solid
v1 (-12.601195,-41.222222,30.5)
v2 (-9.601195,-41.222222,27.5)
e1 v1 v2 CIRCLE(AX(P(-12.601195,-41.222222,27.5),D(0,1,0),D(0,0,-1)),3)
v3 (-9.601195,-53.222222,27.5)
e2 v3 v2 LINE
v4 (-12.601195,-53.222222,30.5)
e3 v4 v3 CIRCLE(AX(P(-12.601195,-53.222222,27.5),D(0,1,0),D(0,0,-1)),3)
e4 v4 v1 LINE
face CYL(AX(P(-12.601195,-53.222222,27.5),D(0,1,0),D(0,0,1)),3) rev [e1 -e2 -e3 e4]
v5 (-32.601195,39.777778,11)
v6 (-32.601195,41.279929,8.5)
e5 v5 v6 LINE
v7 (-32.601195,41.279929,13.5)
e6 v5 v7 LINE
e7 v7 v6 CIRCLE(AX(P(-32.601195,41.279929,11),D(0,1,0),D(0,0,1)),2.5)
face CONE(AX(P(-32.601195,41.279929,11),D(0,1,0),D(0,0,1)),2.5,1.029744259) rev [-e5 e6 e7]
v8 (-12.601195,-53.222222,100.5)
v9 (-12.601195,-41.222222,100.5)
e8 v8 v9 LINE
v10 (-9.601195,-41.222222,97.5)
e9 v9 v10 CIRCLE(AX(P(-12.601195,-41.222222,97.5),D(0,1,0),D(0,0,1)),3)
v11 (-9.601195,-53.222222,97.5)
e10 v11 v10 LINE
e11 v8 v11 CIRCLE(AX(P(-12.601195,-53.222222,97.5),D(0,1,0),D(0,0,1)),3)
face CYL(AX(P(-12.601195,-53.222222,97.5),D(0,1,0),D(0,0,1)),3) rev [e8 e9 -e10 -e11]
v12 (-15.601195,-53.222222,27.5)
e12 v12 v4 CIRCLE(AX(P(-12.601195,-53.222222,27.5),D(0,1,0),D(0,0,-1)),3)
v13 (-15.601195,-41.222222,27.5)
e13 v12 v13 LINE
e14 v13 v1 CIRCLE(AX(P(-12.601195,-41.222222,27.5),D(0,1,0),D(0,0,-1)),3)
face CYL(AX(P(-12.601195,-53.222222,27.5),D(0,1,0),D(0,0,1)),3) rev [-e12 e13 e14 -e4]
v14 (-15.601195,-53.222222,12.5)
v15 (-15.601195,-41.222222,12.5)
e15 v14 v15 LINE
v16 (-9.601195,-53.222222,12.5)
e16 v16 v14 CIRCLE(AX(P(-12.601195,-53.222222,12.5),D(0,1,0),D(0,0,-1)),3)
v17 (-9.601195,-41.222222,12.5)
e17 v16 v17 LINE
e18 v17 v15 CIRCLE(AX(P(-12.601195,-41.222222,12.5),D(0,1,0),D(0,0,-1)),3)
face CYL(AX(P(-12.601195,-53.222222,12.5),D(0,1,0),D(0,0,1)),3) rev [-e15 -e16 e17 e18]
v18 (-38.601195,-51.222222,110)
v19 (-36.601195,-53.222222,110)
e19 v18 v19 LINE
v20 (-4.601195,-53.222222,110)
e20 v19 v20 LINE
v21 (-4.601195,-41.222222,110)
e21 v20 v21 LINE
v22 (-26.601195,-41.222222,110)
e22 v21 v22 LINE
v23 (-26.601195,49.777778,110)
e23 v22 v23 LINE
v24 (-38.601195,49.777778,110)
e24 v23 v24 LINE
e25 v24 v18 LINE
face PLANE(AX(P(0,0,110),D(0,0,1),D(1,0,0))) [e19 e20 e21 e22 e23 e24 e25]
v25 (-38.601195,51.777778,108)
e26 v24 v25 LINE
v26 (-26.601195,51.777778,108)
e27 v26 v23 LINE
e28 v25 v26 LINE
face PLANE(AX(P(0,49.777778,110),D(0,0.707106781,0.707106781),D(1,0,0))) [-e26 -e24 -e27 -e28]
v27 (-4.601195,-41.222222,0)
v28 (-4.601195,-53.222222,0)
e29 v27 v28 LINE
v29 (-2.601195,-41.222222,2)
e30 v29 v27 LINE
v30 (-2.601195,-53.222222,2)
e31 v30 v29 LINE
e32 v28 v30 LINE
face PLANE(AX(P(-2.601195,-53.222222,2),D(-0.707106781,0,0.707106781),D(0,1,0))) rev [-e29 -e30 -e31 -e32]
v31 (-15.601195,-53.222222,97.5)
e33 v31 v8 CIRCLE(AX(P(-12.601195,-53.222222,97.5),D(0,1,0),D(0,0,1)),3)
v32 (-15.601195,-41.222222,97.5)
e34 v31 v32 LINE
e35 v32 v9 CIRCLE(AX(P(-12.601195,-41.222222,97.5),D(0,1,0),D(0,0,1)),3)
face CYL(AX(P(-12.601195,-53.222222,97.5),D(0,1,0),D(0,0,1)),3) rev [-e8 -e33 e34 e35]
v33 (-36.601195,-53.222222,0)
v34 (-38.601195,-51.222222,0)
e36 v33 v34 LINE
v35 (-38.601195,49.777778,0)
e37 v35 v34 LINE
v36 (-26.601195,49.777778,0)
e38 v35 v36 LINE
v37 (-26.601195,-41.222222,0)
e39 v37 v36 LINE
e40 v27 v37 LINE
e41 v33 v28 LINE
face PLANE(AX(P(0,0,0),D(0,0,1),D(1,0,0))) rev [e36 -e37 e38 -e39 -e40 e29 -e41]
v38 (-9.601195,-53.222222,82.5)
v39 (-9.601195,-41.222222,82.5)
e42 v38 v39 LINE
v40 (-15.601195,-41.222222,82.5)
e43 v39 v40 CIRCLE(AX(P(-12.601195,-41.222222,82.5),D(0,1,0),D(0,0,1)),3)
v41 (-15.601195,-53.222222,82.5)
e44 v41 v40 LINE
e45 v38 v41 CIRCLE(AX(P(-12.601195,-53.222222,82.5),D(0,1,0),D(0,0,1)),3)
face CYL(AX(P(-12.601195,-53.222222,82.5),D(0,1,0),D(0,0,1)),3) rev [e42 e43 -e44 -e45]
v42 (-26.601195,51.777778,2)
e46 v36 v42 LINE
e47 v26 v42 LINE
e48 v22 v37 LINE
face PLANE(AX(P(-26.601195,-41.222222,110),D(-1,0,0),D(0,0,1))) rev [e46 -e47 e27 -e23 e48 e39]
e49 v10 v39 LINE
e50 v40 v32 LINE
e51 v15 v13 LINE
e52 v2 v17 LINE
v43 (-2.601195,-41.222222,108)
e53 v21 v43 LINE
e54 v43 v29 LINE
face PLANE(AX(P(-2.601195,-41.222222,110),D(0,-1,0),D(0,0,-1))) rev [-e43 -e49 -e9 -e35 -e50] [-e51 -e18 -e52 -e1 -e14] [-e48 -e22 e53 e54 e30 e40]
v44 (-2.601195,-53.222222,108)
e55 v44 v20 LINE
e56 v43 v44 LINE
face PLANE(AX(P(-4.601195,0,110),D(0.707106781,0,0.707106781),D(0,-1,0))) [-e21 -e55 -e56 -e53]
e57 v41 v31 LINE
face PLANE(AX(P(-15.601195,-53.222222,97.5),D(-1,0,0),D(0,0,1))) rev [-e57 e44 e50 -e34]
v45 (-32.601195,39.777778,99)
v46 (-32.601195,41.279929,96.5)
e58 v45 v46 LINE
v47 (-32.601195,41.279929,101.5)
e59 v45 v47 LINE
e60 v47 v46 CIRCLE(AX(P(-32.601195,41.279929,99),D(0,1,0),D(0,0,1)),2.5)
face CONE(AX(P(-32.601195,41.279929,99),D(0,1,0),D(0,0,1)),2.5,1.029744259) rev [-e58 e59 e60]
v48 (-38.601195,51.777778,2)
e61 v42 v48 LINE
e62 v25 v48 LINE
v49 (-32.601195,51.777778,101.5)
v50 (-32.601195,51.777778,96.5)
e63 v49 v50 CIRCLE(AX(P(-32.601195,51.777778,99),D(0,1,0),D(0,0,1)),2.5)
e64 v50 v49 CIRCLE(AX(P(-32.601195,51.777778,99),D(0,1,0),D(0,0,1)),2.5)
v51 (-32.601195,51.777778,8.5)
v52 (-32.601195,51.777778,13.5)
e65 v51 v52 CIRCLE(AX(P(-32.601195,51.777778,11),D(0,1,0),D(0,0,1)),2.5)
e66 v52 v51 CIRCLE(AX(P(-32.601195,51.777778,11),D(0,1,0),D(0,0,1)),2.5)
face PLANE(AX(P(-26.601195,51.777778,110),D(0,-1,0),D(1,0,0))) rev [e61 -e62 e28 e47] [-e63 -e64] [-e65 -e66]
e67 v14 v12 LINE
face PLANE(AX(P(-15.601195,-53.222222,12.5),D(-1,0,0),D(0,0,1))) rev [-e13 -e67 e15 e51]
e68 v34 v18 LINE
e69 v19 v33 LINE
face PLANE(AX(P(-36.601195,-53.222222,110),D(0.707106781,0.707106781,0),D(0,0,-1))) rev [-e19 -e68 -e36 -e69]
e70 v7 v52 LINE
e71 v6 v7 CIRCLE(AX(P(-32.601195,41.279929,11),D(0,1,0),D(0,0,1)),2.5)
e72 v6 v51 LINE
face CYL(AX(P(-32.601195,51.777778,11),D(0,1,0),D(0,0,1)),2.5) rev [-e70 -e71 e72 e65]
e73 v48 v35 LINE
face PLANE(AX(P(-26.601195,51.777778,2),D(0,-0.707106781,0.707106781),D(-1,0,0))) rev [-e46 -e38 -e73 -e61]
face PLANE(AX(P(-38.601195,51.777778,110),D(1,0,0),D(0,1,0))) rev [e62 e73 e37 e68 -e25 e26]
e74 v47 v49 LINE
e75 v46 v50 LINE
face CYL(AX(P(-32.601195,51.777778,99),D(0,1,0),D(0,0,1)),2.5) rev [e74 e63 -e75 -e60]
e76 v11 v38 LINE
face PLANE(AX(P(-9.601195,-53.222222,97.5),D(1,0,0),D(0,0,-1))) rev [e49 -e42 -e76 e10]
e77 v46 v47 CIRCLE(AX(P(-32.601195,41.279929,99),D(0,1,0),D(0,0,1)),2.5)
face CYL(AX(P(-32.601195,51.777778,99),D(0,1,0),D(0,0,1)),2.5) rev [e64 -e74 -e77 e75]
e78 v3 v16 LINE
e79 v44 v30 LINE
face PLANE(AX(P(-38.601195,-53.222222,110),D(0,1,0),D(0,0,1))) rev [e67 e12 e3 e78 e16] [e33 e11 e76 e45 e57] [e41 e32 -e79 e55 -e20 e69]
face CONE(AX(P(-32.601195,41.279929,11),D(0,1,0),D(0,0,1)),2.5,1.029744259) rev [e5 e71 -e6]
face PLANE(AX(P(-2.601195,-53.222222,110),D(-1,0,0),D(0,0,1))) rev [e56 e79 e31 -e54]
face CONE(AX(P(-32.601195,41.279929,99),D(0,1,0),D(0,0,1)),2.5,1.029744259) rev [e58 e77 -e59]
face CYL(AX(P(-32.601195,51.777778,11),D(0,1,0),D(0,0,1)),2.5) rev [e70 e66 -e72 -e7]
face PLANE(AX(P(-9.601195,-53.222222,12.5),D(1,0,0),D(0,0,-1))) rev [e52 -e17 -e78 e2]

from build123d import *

# Parameters (mm, degrees)
BOSS_EXTRUDE1_DEPTH   = 110
CHAMFER1_SIZE         = 2
CUT_EXTRUDE1_DEPTH    = 150.127637408
M6_TAPPED_HOLE1_D     = 5
M6_TAPPED_HOLE1_DEPTH = 10.497848452
M6_TAPPED_HOLE1_TIP   = 1.502151548


with BuildPart() as part:
    # Sketch1 → Boss-Extrude1 (new body)
    with BuildSketch(Plane.XY):
        Polygon((-38.601194786, 51.777777778), (-38.601194786, -53.222222222), (-2.601194786, -53.222222222), (-2.601194786, -41.222222222), (-26.601194786, -41.222222222), (-26.601194786, 51.777777778), align=None)
    extrude(amount=BOSS_EXTRUDE1_DEPTH)

    # Chamfer1
    chamfer1_edges = [part.edges().sort_by_distance(p)[0] for p in [
        (-38.601194786, -53.222222222, 55),
        (-2.601194786, -47.222222222, 110),
        (-32.601194786, 51.777777778, 110),
        (-2.601194786, -47.222222222, 0),
        (-32.601194786, 51.777777778, 0),
    ]]
    chamfer(chamfer1_edges, length=CHAMFER1_SIZE)

    # Sketch2 → Cut-Extrude1 (cut, through all)
    with BuildSketch(Plane(origin=(0, -41.222222222, 0), x_dir=(1, 0, 0), z_dir=(0, 1, 0))):
        with BuildLine():
            Line((-15.601194786, -97.5), (-15.601194786, -82.5))
            ThreePointArc((-15.601194786, -82.5), (-12.601194786, -79.5), (-9.601194786, -82.5))
            Line((-9.601194786, -82.5), (-9.601194786, -97.5))
            ThreePointArc((-9.601194786, -97.5), (-12.601194786, -100.5), (-15.601194786, -97.5))
        make_face()
        with BuildLine():
            Line((-15.601194786, -12.5), (-15.601194786, -27.5))
            ThreePointArc((-15.601194786, -27.5), (-12.601194786, -30.5), (-9.601194786, -27.5))
            Line((-9.601194786, -27.5), (-9.601194786, -12.5))
            ThreePointArc((-9.601194786, -12.5), (-12.601194786, -9.5), (-15.601194786, -12.5))
        make_face()
    extrude(amount=-CUT_EXTRUDE1_DEPTH, mode=Mode.SUBTRACT)

    # M6 Tapped Hole1
    with Locations(Plane(origin=(0, 51.777777778, 0), x_dir=(1, 0, 0), z_dir=(0, 1, 0))):
        with Locations((-32.601194786, -99), (-32.601194786, -11)):
            Hole(M6_TAPPED_HOLE1_D / 2, depth=M6_TAPPED_HOLE1_DEPTH)
            with Locations((0, 0, -(M6_TAPPED_HOLE1_DEPTH + M6_TAPPED_HOLE1_TIP / 2))):  # 118° drill point
                Cone(0, M6_TAPPED_HOLE1_D / 2, M6_TAPPED_HOLE1_TIP, mode=Mode.SUBTRACT)


solid = part.part
